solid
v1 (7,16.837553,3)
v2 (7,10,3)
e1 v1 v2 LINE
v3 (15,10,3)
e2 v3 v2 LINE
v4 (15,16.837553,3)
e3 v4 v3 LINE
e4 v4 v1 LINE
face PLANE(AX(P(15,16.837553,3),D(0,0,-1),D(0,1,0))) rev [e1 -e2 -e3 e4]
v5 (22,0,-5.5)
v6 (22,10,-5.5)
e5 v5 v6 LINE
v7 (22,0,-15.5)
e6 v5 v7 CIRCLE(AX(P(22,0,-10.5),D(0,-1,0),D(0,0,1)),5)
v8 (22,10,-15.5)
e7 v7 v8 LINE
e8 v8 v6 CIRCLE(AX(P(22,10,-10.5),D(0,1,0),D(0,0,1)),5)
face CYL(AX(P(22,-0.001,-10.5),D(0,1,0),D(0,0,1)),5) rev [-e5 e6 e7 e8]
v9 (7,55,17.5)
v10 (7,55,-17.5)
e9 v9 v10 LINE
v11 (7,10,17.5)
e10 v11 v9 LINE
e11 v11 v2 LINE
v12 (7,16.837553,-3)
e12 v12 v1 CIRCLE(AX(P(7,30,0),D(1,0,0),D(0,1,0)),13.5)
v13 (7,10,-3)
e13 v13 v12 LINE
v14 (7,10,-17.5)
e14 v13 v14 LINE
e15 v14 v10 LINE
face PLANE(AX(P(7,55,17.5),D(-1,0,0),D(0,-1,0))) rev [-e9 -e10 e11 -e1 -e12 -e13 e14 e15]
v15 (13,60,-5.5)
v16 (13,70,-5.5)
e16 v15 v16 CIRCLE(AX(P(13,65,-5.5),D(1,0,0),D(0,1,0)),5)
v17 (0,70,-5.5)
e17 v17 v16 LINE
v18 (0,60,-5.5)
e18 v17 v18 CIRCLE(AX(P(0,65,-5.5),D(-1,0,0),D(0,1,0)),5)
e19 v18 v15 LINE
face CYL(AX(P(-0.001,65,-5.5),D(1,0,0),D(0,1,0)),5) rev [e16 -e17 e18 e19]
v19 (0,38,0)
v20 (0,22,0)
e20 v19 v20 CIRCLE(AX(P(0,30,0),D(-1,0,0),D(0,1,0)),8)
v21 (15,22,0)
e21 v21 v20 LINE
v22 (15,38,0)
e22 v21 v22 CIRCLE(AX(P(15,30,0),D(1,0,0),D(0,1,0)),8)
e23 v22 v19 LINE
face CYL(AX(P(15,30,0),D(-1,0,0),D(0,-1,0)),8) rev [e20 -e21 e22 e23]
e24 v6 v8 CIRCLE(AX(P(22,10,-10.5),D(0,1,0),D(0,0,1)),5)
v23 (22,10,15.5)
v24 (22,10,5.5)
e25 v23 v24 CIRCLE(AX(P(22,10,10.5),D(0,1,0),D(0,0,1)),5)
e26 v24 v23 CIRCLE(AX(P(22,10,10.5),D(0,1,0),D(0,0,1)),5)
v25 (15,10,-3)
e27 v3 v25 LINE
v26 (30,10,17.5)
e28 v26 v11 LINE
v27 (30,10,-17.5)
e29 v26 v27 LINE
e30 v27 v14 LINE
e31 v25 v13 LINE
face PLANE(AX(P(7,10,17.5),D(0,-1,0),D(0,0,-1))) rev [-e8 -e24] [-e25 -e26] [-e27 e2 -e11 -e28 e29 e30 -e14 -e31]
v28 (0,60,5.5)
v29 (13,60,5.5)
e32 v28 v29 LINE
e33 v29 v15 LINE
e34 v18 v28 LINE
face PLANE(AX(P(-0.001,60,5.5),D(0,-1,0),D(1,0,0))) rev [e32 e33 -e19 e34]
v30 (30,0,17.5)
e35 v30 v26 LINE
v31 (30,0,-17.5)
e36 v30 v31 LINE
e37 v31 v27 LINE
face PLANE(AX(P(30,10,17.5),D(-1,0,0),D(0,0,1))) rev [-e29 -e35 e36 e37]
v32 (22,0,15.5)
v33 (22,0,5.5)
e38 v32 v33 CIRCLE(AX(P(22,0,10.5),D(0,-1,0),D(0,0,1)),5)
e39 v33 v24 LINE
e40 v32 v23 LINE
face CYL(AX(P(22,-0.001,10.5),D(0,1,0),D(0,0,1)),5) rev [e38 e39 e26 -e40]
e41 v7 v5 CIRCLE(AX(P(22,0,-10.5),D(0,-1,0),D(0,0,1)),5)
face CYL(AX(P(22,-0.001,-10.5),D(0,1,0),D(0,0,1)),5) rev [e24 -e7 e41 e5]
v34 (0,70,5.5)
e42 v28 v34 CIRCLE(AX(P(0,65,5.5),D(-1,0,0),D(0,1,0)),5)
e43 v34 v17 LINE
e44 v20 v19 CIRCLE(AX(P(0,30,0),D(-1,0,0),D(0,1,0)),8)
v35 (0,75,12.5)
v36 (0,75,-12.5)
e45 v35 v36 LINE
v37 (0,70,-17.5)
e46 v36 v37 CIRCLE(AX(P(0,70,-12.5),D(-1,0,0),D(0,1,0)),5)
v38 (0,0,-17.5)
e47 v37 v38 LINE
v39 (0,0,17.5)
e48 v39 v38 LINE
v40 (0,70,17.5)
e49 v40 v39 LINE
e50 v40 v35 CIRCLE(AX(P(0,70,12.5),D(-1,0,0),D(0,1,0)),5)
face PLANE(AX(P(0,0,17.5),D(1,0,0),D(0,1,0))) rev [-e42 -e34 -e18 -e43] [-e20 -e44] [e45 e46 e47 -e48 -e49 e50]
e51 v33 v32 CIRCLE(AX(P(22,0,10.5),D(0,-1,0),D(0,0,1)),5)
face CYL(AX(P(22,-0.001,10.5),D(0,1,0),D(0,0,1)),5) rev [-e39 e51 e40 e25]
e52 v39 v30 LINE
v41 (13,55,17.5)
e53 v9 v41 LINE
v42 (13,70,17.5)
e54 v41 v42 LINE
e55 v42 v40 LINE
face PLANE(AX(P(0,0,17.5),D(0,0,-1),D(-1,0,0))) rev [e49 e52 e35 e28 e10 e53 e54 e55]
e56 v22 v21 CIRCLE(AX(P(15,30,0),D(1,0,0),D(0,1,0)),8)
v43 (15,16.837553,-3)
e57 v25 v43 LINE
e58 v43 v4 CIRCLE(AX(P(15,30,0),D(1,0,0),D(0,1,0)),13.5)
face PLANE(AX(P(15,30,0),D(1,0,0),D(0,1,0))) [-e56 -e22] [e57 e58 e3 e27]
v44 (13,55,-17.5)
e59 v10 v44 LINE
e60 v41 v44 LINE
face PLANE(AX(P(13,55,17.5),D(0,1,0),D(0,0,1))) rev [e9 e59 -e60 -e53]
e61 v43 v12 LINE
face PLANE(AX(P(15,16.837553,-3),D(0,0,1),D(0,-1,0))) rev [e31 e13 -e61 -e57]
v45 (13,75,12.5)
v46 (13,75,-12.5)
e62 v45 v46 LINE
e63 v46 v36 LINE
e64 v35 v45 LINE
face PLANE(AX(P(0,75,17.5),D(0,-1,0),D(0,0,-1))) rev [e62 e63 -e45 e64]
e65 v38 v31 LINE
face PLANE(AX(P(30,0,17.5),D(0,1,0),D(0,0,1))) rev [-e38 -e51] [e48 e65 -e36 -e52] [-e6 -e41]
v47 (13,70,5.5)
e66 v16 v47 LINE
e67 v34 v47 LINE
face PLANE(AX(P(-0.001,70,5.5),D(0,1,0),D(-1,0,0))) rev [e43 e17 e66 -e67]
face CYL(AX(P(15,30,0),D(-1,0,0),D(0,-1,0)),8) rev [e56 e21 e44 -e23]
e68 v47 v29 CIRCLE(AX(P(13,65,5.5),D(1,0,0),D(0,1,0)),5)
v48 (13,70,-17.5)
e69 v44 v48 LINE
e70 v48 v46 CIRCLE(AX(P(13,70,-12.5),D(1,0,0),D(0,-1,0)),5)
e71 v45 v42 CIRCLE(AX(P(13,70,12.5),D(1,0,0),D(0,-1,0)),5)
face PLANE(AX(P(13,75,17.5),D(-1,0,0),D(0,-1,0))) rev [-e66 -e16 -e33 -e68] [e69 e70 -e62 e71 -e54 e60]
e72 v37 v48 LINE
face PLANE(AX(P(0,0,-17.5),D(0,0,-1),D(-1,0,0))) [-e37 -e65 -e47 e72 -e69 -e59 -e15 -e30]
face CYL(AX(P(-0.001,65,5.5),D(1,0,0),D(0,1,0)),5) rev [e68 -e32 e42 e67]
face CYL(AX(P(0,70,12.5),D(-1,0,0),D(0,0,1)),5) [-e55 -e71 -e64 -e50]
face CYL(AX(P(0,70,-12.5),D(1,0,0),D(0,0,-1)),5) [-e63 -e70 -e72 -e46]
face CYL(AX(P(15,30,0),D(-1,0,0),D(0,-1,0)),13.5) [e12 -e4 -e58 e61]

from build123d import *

# Parameters (mm, degrees)
L_BRACKET_BODY_DEPTH     = 17.5
UPRIGHT_TOP_FILLETS_R5_R = 5
BASE_HOLES_REACH         = 75.697
BASE_HOLES_SKETCH_R      = 5
PIVOT_BOSS_SKETCH_R      = 8
PIVOT_BOSS_DEPTH         = 8
PIVOT_BORE_REACH         = 82.376
SKETCH5_2_R              = 8
TOP_SLOT_REACH           = 80.869


with BuildPart() as part:
    # L Bracket Profile Sketch → L Bracket Body (new, symmetric)
    with BuildSketch(Plane.XY):
        Polygon((0, 0), (0, 75), (13, 75), (13, 55), (7, 55), (7, 10), (30, 10), (30, 0), align=None)
    extrude(amount=L_BRACKET_BODY_DEPTH, both=True)

    # Upright Top Fillets R5
    upright_top_fillets_r5_edges = [part.edges().sort_by_distance(p)[0] for p in [
        (6.5, 75, 17.5),
        (6.5, 75, -17.5),
    ]]
    fillet(upright_top_fillets_r5_edges, radius=UPRIGHT_TOP_FILLETS_R5_R)

    # Base Holes Sketch → Base Holes (cut, up to next)
    with BuildSketch(Plane(origin=(0, 10, 0), x_dir=(1, 0, 0), z_dir=(0, 1, 0)), mode=Mode.PRIVATE) as base_holes_sk1:
        with Locations(Location((22, -10.5, 0), (0, 0, 270))):
            Circle(BASE_HOLES_SKETCH_R)
    base_holes_tool1 = extrude(base_holes_sk1.sketch, amount=-BASE_HOLES_REACH, mode=Mode.PRIVATE) & part.part
    # Base Holes Sketch → Base Holes (cut, up to next)
    with BuildSketch(Plane(origin=(0, 10, 0), x_dir=(1, 0, 0), z_dir=(0, 1, 0)), mode=Mode.PRIVATE) as base_holes_sk2:
        with Locations(Location((22, 10.5, 0), (0, 0, 270))):
            Circle(BASE_HOLES_SKETCH_R)
    base_holes_tool2 = extrude(base_holes_sk2.sketch, amount=-BASE_HOLES_REACH, mode=Mode.PRIVATE) & part.part
    add(base_holes_tool1.solids().sort_by_distance((22, 10, 10.5))[0], mode=Mode.SUBTRACT)
    add(base_holes_tool2.solids().sort_by_distance((22, 10, -10.5))[0], mode=Mode.SUBTRACT)

    # Pivot Boss Sketch → Pivot Boss (add)
    with BuildSketch(Plane(origin=(7, 0, 0), x_dir=(0, 0, -1), z_dir=(1, 0, 0))):
        with BuildLine():
            Line((3, 16.837553419), (3, 10))
            Line((3, 10), (-3, 10))
            Line((-3, 10), (-3, 16.837553419))
            ThreePointArc((-3, 16.837553419), (0, 43.5), (3, 16.837553419))
        make_face()
        with Locations(Location((0, 30, 0), (0, 0, 90))):
            Circle(PIVOT_BOSS_SKETCH_R, mode=Mode.SUBTRACT)
    extrude(amount=PIVOT_BOSS_DEPTH)

    # Sketch5_2 → Pivot Bore (cut, up to next)
    with BuildSketch(Plane(origin=(7, 0, 0), x_dir=(0, 0, -1), z_dir=(1, 0, 0)), mode=Mode.PRIVATE) as pivot_bore_sk1:
        with Locations(Location((0, 30, 0), (0, 0, 90))):
            Circle(SKETCH5_2_R)
    pivot_bore_tool1 = extrude(pivot_bore_sk1.sketch, amount=-PIVOT_BORE_REACH, mode=Mode.PRIVATE) & part.part
    add(pivot_bore_tool1.solids().sort_by_distance((7, 30, 0))[0], mode=Mode.SUBTRACT)

    # Top Slot Sketch → Top Slot (cut, up to next)
    with BuildSketch(Plane(origin=(13, 0, 0), x_dir=(0, 0, -1), z_dir=(1, 0, 0)), mode=Mode.PRIVATE) as top_slot_sk1:
        with BuildLine():
            Line((-5.5, 70), (5.5, 70))
            ThreePointArc((5.5, 70), (10.5, 65), (5.5, 60))
            Line((5.5, 60), (-5.5, 60))
            ThreePointArc((-5.5, 60), (-10.5, 65), (-5.5, 70))
        make_face()
    top_slot_tool1 = extrude(top_slot_sk1.sketch, amount=-TOP_SLOT_REACH, mode=Mode.PRIVATE) & part.part
    add(top_slot_tool1.solids().sort_by_distance((13, 65, 0))[0], mode=Mode.SUBTRACT)


solid = part.part
